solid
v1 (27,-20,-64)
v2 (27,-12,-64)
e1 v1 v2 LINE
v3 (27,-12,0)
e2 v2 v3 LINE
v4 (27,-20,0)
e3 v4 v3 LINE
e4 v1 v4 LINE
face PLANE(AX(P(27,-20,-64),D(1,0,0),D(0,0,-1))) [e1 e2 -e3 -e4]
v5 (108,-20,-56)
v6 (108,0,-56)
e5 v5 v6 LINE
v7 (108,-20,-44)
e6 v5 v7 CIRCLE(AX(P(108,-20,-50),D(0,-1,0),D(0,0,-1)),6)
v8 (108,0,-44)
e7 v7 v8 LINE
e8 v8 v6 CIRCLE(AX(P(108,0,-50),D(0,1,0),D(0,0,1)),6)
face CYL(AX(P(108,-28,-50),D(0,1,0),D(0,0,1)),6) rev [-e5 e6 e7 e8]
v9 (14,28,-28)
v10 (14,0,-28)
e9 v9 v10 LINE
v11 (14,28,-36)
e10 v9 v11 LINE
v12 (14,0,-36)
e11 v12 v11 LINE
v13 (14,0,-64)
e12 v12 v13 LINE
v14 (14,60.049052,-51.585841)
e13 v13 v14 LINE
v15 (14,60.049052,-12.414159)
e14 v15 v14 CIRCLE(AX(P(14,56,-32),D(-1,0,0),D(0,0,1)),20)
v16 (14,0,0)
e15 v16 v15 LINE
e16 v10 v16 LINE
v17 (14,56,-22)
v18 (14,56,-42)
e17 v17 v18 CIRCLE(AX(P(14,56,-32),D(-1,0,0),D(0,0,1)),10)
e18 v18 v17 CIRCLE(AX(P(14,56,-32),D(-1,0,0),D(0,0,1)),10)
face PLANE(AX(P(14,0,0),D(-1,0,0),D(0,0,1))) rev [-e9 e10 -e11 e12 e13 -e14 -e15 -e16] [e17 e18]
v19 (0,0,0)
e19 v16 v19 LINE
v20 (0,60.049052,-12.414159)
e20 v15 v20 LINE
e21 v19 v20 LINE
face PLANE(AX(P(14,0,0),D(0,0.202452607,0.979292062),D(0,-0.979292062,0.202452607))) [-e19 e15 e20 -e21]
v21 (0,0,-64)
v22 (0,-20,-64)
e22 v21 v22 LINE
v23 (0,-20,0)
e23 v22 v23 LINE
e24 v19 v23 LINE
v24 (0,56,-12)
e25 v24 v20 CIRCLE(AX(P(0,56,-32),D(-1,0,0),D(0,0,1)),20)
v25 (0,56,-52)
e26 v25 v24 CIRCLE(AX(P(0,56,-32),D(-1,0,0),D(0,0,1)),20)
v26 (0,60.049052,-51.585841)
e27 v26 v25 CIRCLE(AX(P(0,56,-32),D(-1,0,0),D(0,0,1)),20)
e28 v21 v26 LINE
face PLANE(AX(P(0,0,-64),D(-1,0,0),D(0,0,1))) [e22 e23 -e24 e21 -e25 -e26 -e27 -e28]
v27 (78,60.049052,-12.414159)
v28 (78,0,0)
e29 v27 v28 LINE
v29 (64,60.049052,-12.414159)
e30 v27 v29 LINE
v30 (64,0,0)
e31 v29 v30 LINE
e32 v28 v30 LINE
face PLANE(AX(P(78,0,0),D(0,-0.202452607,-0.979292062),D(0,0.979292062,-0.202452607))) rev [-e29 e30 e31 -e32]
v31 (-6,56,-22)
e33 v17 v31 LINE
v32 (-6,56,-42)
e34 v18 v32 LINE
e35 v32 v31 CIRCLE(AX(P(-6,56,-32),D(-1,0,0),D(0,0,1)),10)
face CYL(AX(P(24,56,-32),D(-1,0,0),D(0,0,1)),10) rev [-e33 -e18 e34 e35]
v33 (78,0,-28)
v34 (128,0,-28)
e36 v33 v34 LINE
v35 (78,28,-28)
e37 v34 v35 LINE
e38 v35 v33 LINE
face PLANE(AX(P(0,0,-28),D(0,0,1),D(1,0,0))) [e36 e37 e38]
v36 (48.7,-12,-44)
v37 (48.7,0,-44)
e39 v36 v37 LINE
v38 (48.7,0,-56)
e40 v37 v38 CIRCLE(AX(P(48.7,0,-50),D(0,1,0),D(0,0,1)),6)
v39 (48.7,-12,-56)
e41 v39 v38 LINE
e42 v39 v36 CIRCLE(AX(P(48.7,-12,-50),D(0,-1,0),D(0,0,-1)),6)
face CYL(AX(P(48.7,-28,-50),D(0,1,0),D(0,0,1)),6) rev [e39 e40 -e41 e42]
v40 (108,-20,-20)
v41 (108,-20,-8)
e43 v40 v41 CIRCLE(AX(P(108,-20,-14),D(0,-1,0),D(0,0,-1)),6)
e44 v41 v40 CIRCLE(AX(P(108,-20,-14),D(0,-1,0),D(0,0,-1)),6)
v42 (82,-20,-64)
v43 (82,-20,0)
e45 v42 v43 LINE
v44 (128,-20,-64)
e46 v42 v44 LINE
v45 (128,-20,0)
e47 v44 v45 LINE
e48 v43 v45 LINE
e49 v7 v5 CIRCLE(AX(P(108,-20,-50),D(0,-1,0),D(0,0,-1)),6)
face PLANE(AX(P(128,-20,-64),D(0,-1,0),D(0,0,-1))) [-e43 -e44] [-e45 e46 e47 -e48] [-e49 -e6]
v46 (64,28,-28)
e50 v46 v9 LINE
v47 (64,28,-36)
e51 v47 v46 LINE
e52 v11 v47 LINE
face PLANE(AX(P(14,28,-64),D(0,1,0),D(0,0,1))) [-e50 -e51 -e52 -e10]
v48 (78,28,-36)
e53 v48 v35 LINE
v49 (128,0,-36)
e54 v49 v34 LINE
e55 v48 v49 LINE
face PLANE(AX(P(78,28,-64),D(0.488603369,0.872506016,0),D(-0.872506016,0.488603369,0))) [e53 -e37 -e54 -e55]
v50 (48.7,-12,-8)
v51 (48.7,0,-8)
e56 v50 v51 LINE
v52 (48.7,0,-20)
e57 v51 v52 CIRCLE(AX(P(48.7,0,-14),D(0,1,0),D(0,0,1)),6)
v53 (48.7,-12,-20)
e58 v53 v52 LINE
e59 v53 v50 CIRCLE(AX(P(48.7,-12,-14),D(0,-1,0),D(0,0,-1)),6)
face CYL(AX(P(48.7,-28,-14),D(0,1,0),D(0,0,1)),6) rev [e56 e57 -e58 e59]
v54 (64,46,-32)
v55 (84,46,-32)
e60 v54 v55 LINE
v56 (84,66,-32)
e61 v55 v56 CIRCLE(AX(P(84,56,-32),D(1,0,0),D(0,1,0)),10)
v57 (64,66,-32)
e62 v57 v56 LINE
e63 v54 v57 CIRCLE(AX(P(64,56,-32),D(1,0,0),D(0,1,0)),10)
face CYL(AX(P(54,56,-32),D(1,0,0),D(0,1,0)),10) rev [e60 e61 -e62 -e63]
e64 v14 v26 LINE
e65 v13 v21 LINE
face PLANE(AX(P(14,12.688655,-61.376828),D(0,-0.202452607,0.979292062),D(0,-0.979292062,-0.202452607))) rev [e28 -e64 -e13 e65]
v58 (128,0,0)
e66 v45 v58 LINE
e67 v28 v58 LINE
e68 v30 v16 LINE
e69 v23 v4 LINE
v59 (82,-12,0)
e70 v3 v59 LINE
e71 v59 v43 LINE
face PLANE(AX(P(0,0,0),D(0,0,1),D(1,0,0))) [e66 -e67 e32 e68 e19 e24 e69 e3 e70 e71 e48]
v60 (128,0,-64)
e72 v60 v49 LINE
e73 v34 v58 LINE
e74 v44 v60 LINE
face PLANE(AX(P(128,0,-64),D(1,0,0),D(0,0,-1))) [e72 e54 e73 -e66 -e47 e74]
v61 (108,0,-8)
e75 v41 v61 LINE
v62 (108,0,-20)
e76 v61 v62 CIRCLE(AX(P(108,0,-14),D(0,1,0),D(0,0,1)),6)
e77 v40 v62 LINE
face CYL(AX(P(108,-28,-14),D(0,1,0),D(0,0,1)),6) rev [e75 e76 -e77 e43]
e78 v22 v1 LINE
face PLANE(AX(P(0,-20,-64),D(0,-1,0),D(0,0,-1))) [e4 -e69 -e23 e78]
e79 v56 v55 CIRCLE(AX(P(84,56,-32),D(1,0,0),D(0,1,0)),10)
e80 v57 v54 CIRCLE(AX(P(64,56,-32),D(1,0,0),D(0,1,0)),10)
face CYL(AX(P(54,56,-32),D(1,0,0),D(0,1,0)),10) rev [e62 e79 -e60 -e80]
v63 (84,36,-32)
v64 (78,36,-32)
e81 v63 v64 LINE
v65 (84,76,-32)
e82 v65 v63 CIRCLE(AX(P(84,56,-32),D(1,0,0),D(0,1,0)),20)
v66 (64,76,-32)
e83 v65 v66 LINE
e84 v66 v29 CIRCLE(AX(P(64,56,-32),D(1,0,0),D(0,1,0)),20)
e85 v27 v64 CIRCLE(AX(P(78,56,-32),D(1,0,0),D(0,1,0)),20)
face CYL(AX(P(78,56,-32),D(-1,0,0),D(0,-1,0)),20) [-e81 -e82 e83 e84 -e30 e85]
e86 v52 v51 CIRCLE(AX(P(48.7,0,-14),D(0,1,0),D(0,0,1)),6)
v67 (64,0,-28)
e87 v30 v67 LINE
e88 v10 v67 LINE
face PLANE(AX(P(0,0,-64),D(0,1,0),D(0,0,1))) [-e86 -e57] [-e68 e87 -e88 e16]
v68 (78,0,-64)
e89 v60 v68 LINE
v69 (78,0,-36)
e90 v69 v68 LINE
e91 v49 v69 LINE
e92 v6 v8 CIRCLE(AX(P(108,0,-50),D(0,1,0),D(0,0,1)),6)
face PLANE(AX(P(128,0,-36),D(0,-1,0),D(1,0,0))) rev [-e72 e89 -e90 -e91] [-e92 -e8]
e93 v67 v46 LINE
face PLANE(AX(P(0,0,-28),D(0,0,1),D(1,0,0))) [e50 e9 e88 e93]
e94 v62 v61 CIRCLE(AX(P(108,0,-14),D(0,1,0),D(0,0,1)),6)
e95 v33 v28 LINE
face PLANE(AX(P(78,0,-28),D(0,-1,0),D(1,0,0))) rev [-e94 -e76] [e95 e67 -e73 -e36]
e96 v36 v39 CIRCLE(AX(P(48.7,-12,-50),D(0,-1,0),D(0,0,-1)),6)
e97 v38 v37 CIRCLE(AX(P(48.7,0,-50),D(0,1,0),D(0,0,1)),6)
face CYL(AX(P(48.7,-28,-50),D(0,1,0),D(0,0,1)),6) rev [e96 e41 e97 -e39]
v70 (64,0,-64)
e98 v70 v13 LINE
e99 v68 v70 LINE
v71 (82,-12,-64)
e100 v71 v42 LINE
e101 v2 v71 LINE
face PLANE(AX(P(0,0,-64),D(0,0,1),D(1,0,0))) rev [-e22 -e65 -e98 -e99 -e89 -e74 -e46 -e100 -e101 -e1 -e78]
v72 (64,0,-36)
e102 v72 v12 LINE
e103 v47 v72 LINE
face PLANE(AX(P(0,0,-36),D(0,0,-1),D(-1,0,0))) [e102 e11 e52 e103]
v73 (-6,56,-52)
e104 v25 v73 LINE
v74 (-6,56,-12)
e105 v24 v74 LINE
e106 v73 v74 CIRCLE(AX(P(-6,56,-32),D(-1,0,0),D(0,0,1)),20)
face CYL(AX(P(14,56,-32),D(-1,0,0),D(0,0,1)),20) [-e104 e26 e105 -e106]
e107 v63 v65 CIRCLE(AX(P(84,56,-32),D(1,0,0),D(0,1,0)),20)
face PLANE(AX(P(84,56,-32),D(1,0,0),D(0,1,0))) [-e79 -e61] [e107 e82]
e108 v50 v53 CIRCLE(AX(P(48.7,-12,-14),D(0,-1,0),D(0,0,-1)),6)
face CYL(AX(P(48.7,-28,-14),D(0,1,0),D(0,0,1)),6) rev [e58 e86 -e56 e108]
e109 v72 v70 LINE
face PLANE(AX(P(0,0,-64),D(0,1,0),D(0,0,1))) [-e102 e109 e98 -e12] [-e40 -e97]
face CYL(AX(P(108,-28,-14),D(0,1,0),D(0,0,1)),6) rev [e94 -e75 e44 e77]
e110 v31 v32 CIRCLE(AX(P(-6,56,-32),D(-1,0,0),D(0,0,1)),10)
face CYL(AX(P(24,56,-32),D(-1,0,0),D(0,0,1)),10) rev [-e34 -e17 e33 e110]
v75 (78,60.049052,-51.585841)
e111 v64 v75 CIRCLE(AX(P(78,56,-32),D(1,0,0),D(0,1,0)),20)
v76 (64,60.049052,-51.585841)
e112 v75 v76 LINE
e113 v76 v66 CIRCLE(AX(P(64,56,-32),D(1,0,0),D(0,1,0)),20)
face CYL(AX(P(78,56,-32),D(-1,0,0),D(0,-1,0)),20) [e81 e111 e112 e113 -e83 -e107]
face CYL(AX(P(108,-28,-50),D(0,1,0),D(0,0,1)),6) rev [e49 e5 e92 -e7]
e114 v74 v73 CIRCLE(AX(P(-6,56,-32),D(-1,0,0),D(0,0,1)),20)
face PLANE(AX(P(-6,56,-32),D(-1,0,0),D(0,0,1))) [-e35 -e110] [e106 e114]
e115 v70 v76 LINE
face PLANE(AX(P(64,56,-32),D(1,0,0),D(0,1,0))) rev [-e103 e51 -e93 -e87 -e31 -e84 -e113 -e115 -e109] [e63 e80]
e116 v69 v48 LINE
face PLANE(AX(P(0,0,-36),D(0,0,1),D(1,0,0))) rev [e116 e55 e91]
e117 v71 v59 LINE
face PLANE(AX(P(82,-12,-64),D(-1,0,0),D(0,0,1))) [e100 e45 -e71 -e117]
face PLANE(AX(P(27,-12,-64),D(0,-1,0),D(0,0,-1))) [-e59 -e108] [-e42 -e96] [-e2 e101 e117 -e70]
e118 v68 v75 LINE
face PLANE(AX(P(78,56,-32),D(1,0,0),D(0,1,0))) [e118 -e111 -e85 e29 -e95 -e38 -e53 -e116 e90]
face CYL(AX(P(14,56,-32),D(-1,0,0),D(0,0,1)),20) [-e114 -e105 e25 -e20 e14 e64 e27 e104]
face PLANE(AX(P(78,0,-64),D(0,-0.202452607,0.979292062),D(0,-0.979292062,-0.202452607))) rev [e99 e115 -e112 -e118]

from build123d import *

# Parameters (mm, degrees)
BASE_PLATE_DEPTH        = 64
CLEVIS_LUG_1_DEPTH      = 14
LUG_START               = 6
LUG_1_HUB_SKETCH_R      = 20
LUG_1_HUB_BOSS_40_DEPTH = 6
LUG_1_PIN_BORE_SKETCH_R = 10
LUG_1_PIN_BORE_20_DEPTH = 30
WEB_BLOCK_SKETCH_W      = 50
WEB_BLOCK_SKETCH_H      = 28
WEB_BLOCK_DEPTH         = 64
WEB_TRIM_CUT_1_SKETCH_W = 50
WEB_TRIM_CUT_1_SKETCH_H = 28
WEB_TRIM_CUT_1_DEPTH    = 28
WEB_TRIM_CUT_2_SKETCH_W = 50
WEB_TRIM_CUT_2_SKETCH_H = 28
WEB_TRIM_CUT_2_DEPTH    = 28
CLEVIS_LUG_2_DEPTH      = 14
LUG_2_HUB_SKETCH_R      = 20
LUG_2_HUB_BOSS_40_DEPTH = 6
LUG_START_2             = -30
LUG_2_PIN_BORE_SKETCH_R = 10
LUG_2_PIN_BORE_20_DEPTH = 30
GUSSET_BLOCK_DEPTH      = 64
GUSSET_TRIM_CUT_1_DEPTH = 28
GUSSET_TRIM_CUT_2_DEPTH = 28
MOUNTING_HOLES_SKETCH_R = 6
MOUNTING_HOLES_12_DEPTH = 28


with BuildPart() as part:
    # Base Plate Profile Sketch → Base Plate (new body)
    with BuildSketch(Plane.XY):
        Polygon((0, 0), (27, 0), (82, 0), (128, 0), (128, -20), (82, -20), (82, -12), (27, -12), (27, -20), (0, -20), align=None)
    extrude(amount=-BASE_PLATE_DEPTH)

    # Clevis Lug 1 Sketch → Clevis Lug 1 (add)
    with BuildSketch(Plane.ZY):
        with BuildLine():
            Line((-51.585841233, 60.049052133), (-64, 0))
            Line((-64, 0), (-32, 0))
            Line((-32, 0), (0, 0))
            Line((0, 0), (-12.414158767, 60.049052133))
            ThreePointArc((-12.414158767, 60.049052133), (-32, 76), (-51.585841233, 60.049052133))
        make_face()
    extrude(amount=-CLEVIS_LUG_1_DEPTH)

    # Lug 1 Hub Sketch → Lug 1 Hub Boss Ø40 (add)
    with BuildSketch(Plane.ZY.offset(LUG_START)):
        with Locations((-32, 56)):
            Circle(LUG_1_HUB_SKETCH_R)
    extrude(amount=-LUG_1_HUB_BOSS_40_DEPTH)

    # Lug 1 Pin Bore Sketch → Lug 1 Pin Bore Ø20 (cut)
    with BuildSketch(Plane.ZY.offset(6)):
        with Locations((-32, 56)):
            Circle(LUG_1_PIN_BORE_SKETCH_R)
    extrude(amount=-LUG_1_PIN_BORE_20_DEPTH, mode=Mode.SUBTRACT)

    # Web Block Sketch → Web Block (add)
    with BuildSketch(Plane.XY):
        with Locations((39, 14)):
            Rectangle(WEB_BLOCK_SKETCH_W, WEB_BLOCK_SKETCH_H)
    extrude(amount=-WEB_BLOCK_DEPTH)

    # Web Trim Cut 1 Sketch → Web Trim Cut 1 (cut)
    with BuildSketch(Plane.XY):
        with Locations((39, 14)):
            Rectangle(WEB_TRIM_CUT_1_SKETCH_W, WEB_TRIM_CUT_1_SKETCH_H)
    extrude(amount=-WEB_TRIM_CUT_1_DEPTH, mode=Mode.SUBTRACT)

    # Web Trim Cut 2 Sketch → Web Trim Cut 2 (cut)
    with BuildSketch(Plane(origin=(0, 0, -64), x_dir=(-1, 0, 0), z_dir=(0, 0, -1))):
        with Locations((-39, 14)):
            Rectangle(WEB_TRIM_CUT_2_SKETCH_W, WEB_TRIM_CUT_2_SKETCH_H)
    extrude(amount=-WEB_TRIM_CUT_2_DEPTH, mode=Mode.SUBTRACT)

    # Clevis Lug 2 Sketch → Clevis Lug 2 (add)
    with BuildSketch(Plane(origin=(64, 0, 0), x_dir=(0, 0, -1), z_dir=(1, 0, 0))):
        with BuildLine():
            Line((0, 0), (12.414158767, 60.049052133))
            ThreePointArc((12.414158767, 60.049052133), (32, 76), (51.585841233, 60.049052133))
            Line((51.585841233, 60.049052133), (64, 0))
            Line((64, 0), (0, 0))
        make_face()
    extrude(amount=CLEVIS_LUG_2_DEPTH)

    # Lug 2 Hub Sketch → Lug 2 Hub Boss Ø40 (add)
    with BuildSketch(Plane(origin=(78, 0, 0), x_dir=(0, 0, -1), z_dir=(1, 0, 0))):
        with Locations(Location((32, 56, 0), (0, 0, 180))):
            Circle(LUG_2_HUB_SKETCH_R)
    extrude(amount=LUG_2_HUB_BOSS_40_DEPTH)

    # Lug 2 Pin Bore Sketch → Lug 2 Pin Bore Ø20 (cut)
    with BuildSketch(Plane(origin=(84, 0, 0), x_dir=(0, 0, -1), z_dir=(1, 0, 0)).offset(LUG_START_2)):
        with Locations(Location((32, 56, 0), (0, 0, 180))):
            Circle(LUG_2_PIN_BORE_SKETCH_R)
    extrude(amount=LUG_2_PIN_BORE_20_DEPTH, mode=Mode.SUBTRACT)

    # Gusset Block Sketch → Gusset Block (add)
    with BuildSketch(Plane.XY):
        Polygon((78, 0), (78, 28), (128, 0), align=None)
    extrude(amount=-GUSSET_BLOCK_DEPTH)

    # Gusset Trim Cut 1 Sketch → Gusset Trim Cut 1 (cut)
    with BuildSketch(Plane.XY):
        Polygon((78, 28), (78, 0), (128, 0), align=None)
    extrude(amount=-GUSSET_TRIM_CUT_1_DEPTH, mode=Mode.SUBTRACT)

    # Gusset Trim Cut 2 Sketch → Gusset Trim Cut 2 (cut)
    with BuildSketch(Plane(origin=(0, 0, -64), x_dir=(-1, 0, 0), z_dir=(0, 0, -1))):
        Polygon((-128, 0), (-78, 0), (-78, 28), align=None)
    extrude(amount=-GUSSET_TRIM_CUT_2_DEPTH, mode=Mode.SUBTRACT)

    # Mounting Holes Sketch → Mounting Holes Ø12 (cut)
    with BuildSketch(Plane(origin=(0, 0, 0), x_dir=(1, 0, 0), z_dir=(0, 1, 0))):
        with Locations(Location((48.7, 50, 0), (0, 0, 270))):
            Circle(MOUNTING_HOLES_SKETCH_R)
        with Locations(Location((108, 50, 0), (0, 0, 270))):
            Circle(MOUNTING_HOLES_SKETCH_R)
        with Locations(Location((108, 14, 0), (0, 0, 270))):
            Circle(MOUNTING_HOLES_SKETCH_R)
        with Locations(Location((48.7, 14, 0), (0, 0, 270))):
            Circle(MOUNTING_HOLES_SKETCH_R)
    extrude(amount=-MOUNTING_HOLES_12_DEPTH, mode=Mode.SUBTRACT)


solid = part.part
